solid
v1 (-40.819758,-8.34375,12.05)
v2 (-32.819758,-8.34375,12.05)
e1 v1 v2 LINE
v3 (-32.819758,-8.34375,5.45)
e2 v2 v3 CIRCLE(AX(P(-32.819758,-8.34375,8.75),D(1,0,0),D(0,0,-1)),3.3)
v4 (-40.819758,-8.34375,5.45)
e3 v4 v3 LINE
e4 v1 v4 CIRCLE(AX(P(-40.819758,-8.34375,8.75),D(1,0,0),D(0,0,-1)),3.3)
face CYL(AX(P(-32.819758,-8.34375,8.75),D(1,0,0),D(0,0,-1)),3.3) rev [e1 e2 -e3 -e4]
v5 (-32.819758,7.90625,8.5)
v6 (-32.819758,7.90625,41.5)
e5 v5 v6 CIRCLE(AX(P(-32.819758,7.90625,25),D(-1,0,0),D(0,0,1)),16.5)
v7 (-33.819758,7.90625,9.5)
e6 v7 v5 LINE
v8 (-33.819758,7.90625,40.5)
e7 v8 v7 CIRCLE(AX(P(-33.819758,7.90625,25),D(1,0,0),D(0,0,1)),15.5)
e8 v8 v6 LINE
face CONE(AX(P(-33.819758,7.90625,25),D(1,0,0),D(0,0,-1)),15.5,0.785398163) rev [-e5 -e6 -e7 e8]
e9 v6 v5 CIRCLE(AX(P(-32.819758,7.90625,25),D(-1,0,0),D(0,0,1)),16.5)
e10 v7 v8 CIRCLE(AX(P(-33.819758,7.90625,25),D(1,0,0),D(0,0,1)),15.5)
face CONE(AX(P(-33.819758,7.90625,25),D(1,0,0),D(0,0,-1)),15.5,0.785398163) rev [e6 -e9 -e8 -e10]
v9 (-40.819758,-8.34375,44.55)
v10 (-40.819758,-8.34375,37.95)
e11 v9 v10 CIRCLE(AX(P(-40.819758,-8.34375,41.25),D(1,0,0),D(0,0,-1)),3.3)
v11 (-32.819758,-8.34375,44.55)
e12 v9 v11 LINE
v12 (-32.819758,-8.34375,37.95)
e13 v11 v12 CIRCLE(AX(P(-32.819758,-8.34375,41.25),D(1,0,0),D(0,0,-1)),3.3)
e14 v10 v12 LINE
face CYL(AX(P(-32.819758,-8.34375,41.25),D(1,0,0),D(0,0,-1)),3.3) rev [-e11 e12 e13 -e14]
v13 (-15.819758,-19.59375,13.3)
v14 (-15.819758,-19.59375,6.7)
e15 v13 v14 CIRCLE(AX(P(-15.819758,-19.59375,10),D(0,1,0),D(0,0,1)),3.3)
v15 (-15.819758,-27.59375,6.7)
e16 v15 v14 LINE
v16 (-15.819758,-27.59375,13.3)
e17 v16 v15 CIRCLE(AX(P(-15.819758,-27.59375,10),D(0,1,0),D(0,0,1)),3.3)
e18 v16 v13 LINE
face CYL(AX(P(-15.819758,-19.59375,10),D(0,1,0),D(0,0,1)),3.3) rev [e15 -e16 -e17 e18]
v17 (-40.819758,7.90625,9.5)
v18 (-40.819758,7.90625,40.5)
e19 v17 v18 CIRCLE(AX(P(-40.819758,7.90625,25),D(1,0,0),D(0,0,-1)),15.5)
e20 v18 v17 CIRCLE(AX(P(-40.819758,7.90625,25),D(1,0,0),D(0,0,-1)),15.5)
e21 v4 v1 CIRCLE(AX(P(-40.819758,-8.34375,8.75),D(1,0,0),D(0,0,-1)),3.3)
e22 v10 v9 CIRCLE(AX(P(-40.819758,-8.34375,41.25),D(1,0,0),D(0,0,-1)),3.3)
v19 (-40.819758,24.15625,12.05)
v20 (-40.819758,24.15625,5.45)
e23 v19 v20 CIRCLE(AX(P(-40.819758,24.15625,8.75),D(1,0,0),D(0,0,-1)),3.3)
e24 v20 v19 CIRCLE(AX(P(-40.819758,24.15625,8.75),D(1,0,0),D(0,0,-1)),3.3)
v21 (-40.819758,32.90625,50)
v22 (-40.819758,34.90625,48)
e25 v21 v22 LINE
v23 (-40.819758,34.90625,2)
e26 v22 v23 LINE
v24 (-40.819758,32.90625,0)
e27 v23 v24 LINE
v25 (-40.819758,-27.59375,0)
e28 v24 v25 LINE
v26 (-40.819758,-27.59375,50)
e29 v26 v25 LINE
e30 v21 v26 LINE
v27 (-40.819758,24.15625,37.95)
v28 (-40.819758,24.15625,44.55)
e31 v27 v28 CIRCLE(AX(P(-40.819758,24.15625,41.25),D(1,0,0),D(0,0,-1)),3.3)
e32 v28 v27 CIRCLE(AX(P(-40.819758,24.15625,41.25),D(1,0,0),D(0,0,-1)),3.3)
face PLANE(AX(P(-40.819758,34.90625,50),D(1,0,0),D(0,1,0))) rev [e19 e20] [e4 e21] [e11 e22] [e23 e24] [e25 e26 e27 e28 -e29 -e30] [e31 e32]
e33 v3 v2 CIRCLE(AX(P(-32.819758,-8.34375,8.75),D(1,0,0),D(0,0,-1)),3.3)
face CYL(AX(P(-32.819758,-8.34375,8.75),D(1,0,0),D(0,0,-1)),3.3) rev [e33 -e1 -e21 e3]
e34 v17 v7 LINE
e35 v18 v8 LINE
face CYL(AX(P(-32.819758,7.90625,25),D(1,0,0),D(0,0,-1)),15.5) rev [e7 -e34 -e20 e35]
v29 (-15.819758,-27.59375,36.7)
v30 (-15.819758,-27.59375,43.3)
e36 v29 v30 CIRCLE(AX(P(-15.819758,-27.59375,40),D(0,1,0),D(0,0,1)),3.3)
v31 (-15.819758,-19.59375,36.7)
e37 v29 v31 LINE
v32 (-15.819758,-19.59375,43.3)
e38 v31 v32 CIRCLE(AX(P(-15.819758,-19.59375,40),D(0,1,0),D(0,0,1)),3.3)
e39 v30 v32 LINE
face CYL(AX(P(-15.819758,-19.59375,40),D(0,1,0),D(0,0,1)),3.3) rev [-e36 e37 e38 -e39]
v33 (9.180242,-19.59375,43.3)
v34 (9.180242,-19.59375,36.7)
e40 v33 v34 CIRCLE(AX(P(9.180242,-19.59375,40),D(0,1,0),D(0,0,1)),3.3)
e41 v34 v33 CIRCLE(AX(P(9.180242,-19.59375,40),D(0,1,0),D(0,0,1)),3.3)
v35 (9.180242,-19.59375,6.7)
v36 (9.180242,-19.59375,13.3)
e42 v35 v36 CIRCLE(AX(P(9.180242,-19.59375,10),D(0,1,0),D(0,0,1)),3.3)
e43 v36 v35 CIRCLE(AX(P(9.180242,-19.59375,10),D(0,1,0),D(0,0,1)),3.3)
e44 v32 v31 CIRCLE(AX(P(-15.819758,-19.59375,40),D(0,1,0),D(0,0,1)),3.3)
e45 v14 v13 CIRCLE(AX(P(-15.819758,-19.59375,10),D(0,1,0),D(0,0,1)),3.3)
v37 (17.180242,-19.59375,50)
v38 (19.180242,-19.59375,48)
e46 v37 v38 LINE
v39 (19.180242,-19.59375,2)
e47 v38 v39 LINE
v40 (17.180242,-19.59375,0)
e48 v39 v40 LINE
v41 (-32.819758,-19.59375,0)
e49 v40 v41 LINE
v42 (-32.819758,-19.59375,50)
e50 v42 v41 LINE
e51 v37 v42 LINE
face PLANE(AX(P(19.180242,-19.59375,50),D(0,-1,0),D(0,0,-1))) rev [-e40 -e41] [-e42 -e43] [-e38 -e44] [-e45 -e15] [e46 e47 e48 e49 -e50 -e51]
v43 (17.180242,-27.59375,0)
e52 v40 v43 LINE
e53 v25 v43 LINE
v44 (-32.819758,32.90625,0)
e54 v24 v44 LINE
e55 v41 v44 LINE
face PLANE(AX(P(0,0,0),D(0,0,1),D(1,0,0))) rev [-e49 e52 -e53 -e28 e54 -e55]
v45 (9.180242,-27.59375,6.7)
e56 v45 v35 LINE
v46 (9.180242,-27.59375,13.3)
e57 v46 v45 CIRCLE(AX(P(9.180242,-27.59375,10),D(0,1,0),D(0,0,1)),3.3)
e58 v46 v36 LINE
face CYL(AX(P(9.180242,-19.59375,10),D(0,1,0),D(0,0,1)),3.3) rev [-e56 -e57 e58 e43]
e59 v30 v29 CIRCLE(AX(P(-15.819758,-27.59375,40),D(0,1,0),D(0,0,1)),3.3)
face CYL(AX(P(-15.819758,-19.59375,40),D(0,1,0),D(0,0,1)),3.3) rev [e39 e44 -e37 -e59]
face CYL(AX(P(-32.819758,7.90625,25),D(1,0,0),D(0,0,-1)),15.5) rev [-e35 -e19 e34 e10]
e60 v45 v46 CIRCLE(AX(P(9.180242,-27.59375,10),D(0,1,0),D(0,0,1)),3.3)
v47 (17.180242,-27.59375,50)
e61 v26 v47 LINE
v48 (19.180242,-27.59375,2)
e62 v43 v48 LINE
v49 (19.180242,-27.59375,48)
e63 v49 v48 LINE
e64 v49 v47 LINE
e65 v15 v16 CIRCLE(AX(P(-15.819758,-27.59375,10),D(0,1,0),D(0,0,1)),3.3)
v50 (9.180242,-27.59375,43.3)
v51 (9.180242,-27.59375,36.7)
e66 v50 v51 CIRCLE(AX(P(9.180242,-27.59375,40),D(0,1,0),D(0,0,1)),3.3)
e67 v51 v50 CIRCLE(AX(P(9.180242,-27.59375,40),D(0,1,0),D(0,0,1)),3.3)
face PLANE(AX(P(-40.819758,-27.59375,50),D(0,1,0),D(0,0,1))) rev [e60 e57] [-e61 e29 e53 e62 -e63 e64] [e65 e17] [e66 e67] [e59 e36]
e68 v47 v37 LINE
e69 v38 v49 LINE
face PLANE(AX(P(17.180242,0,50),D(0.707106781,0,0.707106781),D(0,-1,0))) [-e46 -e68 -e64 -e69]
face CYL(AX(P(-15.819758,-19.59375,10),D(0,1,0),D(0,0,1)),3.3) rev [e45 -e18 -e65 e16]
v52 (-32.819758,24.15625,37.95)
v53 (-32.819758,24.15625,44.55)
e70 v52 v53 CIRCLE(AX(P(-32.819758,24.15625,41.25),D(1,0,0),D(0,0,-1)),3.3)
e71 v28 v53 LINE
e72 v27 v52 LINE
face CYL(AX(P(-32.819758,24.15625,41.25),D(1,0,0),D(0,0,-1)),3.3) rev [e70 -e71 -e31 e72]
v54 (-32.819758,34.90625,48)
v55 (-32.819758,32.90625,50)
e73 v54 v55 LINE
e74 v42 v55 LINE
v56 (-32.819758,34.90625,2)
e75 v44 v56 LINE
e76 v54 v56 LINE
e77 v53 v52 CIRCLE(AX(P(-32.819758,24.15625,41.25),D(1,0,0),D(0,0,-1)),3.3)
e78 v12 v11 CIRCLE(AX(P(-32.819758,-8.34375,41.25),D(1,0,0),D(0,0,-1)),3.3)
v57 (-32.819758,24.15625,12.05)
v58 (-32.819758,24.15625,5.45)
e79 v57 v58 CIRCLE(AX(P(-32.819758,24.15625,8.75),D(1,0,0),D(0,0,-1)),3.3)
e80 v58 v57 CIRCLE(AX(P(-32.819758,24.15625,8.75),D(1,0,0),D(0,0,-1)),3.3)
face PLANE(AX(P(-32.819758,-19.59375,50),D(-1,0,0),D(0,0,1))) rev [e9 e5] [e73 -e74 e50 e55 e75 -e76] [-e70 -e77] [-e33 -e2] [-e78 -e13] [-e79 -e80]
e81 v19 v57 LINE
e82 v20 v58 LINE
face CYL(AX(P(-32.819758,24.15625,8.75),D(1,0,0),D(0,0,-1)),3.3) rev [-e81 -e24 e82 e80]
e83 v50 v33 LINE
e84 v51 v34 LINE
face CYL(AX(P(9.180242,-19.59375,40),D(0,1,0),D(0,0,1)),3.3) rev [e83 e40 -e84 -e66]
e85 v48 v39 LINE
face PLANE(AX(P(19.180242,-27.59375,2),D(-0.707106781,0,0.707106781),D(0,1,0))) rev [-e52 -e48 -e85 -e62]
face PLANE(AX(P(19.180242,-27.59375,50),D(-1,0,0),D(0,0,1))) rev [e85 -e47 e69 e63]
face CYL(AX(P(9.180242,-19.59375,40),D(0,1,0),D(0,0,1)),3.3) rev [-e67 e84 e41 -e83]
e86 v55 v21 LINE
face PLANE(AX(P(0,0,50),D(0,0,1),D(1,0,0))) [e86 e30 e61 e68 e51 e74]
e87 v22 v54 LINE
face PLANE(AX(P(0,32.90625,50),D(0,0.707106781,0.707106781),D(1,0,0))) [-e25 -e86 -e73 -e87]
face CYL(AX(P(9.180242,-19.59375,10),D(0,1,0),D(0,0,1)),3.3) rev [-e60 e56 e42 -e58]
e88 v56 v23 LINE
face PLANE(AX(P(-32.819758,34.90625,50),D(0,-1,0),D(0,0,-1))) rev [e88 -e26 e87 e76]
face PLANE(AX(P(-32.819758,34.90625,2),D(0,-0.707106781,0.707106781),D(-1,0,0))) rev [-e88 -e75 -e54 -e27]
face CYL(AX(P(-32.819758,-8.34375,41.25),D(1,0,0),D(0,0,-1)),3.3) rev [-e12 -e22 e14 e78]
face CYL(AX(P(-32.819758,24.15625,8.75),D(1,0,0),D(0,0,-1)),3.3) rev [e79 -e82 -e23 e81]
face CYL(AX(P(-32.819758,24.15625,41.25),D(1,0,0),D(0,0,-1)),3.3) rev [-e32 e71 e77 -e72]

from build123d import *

# Parameters (mm, degrees)
BOSS_EXTRUDE1_DEPTH = 50
HOLE1_D             = 6.6
HOLE2_D             = 31
CHAMFER1_SIZE       = 1
CHAMFER2_SIZE       = 2
HOLE3_D             = 6.6


with BuildPart() as part:
    # Sketch1 → Boss-Extrude1 (new body)
    with BuildSketch(Plane.XY):
        Polygon((-40.819758101, 34.90625), (-40.819758101, -27.59375), (19.180241899, -27.59375), (19.180241899, -19.59375), (-32.819758101, -19.59375), (-32.819758101, 34.90625), align=None)
    extrude(amount=BOSS_EXTRUDE1_DEPTH)

    # Hole1 (through all)
    with Locations(Plane(origin=(-32.819758101, 0, 0), x_dir=(0, 0, -1), z_dir=(1, 0, 0))):
        with Locations((-41.25, 24.15625), (-8.75, 24.15625), (-8.75, -8.34375), (-41.25, -8.34375)):
            Hole(HOLE1_D / 2)

    # Hole2 (through all)
    with Locations(Plane(origin=(-32.819758101, 0, 0), x_dir=(0, 0, -1), z_dir=(1, 0, 0))):
        with Locations((-25, 7.90625)):
            Hole(HOLE2_D / 2)

    # Chamfer1
    chamfer1_edges = [part.edges().sort_by_distance(p)[0] for p in [
        (-32.819758101, 7.90625, 9.5),
    ]]
    chamfer(chamfer1_edges, length=CHAMFER1_SIZE)

    # Chamfer2
    chamfer2_edges = [part.edges().sort_by_distance(p)[0] for p in [
        (19.180241899, -23.59375, 50),
        (-36.819758101, 34.90625, 50),
        (19.180241899, -23.59375, 0),
        (-36.819758101, 34.90625, 0),
    ]]
    chamfer(chamfer2_edges, length=CHAMFER2_SIZE)

    # Hole3 (through all)
    with Locations(Plane(origin=(0, -19.59375, 0), x_dir=(1, 0, 0), z_dir=(0, 1, 0))):
        with Locations((-15.819758101, -40), (-15.819758101, -10), (9.180241899, -10), (9.180241899, -40)):
            Hole(HOLE3_D / 2)


solid = part.part
